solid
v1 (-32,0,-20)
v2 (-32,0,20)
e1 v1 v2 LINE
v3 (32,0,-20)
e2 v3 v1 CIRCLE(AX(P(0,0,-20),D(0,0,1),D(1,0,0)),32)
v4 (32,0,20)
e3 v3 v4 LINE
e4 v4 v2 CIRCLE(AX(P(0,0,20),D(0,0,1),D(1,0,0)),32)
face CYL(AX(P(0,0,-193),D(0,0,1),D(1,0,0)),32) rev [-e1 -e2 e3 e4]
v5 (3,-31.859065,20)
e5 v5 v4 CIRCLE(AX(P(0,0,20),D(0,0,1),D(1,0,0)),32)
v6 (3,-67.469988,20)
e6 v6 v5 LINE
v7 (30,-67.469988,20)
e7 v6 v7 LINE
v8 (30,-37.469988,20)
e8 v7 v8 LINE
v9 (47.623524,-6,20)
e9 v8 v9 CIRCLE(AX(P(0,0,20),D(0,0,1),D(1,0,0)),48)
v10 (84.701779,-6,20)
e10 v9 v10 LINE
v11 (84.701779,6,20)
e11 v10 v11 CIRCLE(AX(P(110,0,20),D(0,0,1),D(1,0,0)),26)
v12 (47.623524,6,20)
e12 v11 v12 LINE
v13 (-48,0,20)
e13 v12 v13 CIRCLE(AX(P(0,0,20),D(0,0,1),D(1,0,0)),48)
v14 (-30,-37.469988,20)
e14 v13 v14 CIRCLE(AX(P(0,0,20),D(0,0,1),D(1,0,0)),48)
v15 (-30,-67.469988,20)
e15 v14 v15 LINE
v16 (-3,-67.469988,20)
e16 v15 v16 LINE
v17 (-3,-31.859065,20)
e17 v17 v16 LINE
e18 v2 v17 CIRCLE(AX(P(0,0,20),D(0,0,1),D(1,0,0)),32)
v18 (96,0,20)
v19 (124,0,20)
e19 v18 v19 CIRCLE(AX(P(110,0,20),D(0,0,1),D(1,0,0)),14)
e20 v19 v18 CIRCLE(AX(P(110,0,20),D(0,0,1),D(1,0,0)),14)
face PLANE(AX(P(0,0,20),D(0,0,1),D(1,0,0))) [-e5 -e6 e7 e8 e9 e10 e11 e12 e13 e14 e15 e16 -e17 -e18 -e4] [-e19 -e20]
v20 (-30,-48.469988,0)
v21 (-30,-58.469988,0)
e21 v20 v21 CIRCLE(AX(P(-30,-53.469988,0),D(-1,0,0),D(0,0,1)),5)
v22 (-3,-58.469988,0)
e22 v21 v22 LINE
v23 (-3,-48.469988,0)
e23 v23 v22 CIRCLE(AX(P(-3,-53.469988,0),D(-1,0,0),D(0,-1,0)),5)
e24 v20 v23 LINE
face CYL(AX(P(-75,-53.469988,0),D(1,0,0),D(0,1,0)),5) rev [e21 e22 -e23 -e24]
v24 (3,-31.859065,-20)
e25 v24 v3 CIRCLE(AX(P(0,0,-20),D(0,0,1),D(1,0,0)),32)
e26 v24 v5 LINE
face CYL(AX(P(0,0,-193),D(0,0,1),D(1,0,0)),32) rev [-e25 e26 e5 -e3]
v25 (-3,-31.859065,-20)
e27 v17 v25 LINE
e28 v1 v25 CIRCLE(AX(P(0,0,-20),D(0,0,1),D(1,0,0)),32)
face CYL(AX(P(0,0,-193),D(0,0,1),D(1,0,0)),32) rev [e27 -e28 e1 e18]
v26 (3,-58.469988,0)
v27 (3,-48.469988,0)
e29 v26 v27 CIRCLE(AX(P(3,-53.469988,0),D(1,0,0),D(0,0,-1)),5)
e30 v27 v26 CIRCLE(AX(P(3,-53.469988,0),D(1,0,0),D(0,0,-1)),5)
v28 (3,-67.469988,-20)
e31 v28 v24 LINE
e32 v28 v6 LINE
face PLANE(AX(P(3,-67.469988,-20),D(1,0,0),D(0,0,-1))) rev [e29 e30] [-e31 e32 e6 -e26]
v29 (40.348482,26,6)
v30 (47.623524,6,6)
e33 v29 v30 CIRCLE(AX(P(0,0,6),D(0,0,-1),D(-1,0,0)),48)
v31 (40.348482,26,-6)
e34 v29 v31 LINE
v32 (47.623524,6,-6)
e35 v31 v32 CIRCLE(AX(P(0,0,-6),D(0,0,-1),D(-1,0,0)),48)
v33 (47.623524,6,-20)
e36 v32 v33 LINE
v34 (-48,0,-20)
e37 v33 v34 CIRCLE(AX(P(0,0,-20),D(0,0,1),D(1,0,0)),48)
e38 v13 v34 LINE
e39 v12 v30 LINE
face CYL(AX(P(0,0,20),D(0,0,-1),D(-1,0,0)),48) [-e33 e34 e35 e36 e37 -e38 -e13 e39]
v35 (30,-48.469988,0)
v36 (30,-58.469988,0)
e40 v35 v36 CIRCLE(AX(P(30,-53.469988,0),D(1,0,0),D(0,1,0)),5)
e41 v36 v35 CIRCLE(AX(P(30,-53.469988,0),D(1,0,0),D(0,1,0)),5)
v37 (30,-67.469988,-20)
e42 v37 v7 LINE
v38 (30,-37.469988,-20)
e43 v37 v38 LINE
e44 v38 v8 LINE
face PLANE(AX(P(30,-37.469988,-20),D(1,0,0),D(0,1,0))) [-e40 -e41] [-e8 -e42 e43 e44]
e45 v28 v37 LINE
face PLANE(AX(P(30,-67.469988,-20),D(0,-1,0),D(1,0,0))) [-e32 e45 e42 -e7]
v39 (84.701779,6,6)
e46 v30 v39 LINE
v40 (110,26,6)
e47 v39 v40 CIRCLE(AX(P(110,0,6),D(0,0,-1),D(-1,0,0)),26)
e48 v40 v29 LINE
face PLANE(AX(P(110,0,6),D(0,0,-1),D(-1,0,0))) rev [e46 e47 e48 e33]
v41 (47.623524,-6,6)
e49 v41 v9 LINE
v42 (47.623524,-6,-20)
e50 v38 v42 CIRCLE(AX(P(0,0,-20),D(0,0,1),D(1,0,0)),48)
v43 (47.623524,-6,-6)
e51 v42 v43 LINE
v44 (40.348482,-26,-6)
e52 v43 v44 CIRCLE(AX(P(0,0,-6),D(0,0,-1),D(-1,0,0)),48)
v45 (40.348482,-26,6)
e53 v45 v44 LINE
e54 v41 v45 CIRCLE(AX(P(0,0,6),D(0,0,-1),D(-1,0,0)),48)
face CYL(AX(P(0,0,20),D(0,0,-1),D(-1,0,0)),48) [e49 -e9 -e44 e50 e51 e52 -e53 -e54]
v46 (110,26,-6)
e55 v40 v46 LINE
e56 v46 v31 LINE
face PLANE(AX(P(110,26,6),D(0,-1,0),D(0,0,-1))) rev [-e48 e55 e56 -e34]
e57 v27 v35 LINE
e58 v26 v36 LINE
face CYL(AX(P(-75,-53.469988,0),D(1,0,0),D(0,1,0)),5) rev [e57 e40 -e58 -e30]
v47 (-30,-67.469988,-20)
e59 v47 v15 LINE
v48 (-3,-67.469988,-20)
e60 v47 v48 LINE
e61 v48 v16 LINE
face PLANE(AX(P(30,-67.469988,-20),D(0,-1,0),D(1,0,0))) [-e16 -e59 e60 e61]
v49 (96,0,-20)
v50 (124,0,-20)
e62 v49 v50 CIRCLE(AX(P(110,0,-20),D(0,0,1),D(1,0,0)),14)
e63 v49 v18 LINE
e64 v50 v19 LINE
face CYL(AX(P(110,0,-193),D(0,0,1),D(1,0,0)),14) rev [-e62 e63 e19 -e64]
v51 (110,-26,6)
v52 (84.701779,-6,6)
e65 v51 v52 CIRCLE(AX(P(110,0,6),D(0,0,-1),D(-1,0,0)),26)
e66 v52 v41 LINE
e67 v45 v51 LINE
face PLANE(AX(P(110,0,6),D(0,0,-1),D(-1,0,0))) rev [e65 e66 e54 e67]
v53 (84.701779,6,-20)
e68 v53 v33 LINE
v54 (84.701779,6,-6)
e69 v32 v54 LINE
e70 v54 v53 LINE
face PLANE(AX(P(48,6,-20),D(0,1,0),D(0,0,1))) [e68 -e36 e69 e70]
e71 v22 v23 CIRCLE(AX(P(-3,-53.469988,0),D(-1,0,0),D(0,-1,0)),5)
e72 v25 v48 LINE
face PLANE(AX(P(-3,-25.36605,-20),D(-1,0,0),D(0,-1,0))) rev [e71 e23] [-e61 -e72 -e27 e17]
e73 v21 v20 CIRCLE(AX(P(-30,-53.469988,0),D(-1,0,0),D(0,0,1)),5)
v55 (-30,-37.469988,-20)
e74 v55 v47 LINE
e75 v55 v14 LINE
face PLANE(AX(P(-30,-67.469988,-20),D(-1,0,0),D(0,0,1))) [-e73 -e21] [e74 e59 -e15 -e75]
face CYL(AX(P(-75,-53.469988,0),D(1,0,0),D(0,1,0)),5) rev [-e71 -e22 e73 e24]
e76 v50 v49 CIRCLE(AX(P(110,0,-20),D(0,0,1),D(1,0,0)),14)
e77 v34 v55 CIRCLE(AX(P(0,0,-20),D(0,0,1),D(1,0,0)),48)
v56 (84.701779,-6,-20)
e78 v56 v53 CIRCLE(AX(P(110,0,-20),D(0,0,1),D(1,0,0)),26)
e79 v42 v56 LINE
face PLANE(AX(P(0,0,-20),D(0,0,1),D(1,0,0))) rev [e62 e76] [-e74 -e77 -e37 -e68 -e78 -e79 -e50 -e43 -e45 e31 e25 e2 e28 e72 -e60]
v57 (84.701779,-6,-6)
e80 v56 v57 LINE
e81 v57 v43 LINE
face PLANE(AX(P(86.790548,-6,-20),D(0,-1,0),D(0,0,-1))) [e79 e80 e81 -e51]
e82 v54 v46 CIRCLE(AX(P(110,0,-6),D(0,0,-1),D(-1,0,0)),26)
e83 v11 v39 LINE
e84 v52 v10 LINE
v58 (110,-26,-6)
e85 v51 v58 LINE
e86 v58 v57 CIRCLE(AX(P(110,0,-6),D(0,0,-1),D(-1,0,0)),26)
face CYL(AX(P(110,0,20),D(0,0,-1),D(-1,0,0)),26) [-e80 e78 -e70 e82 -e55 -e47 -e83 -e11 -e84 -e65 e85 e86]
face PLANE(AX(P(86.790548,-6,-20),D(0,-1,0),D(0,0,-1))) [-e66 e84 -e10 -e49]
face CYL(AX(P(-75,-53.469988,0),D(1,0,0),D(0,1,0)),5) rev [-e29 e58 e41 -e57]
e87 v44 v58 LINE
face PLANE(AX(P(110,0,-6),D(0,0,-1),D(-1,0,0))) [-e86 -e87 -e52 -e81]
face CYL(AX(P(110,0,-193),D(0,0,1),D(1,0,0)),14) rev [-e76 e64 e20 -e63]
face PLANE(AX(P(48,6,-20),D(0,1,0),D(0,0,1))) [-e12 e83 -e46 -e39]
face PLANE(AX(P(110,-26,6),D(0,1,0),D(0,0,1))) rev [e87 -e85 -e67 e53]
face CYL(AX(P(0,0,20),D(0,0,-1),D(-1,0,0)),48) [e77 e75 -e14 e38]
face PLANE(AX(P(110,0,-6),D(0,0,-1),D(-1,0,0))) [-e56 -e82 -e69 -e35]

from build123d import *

# Parameters (mm, degrees)
CLAMP_RING_PROFILE_R       = 48
CLAMP_RING_96_DEPTH        = 20
END_BOSS_PROFILE_R         = 26
END_BOSS_52_DEPTH          = 20
LEVER_WEB_DEPTH            = 40
RIB_A_DEPTH                = 6
RIB_B_DEPTH                = 6
CLAMP_BORE_PROFILE_R       = 32
CLAMP_BORE_DEPTH           = 213
END_BORE_PROFILE_R         = 14
END_BORE_DEPTH             = 213
CLAMP_LUG_DEPTH            = 40
CLAMP_SLOT_DEPTH           = 40
CLAMP_SCREW_HOLE_PROFILE_R = 5
CLAMP_SCREW_HOLE_DEPTH     = 105


with BuildPart() as part:
    # Clamp Ring Profile → Clamp Ring Ø96 (new, symmetric)
    with BuildSketch(Plane.XY):
        Circle(CLAMP_RING_PROFILE_R)
    extrude(amount=CLAMP_RING_96_DEPTH, both=True)



with BuildPart() as body_2:
    # End Boss Profile → End Boss Ø52 (new, symmetric)
    with BuildSketch(Plane.XY):
        with Locations((110, 0)):
            Circle(END_BOSS_PROFILE_R)
    extrude(amount=END_BOSS_52_DEPTH, both=True)


with BuildPart() as part_1:
    add(part.part)

    add(body_2.part)  # Lever Web merges body 2
    # Lever Web Profile → Lever Web (add)
    with BuildSketch(Plane.XY.offset(20)):
        Polygon((48, 6), (86.790548166, 6), (86.790548166, -6), (44, -6), (44, 6), align=None)
    extrude(amount=-LEVER_WEB_DEPTH)

    # Rib A Profile → Rib A (add, symmetric)
    with BuildSketch(Plane.XY):
        with BuildLine():
            Line((110, 26), (40.348482004, 26))
            ThreePointArc((40.348482004, 26), (45.108407669, 16.408277105), (47.623523599, 6))
            Line((47.623523599, 6), (84.701778719, 6))
            ThreePointArc((84.701778719, 6), (93.875484503, 20.396078054), (110, 26))
        make_face()
    extrude(amount=RIB_A_DEPTH, both=True)

    # Rib B Profile → Rib B (add, symmetric)
    with BuildSketch(Plane.XY):
        with BuildLine():
            Line((110, -26), (40.276028999, -26))
            ThreePointArc((40.276028999, -26), (45.014976817, -16.391327753), (47.623523599, -6))
            Line((47.623523599, -6), (84.701778719, -6))
            ThreePointArc((84.701778719, -6), (93.875484503, -20.396078054), (110, -26))
        make_face()
    extrude(amount=RIB_B_DEPTH, both=True)

    # Clamp Bore Profile → Clamp Bore (cut)
    with BuildSketch(Plane.XY.offset(20)):
        Circle(CLAMP_BORE_PROFILE_R)
    extrude(amount=-CLAMP_BORE_DEPTH, mode=Mode.SUBTRACT)

    # End Bore Profile → End Bore (cut)
    with BuildSketch(Plane.XY.offset(20)):
        with Locations((110, 0)):
            Circle(END_BORE_PROFILE_R)
    extrude(amount=-END_BORE_DEPTH, mode=Mode.SUBTRACT)

    # Clamp Lug Profile → Clamp Lug (add)
    with BuildSketch(Plane.XY.offset(20)):
        Polygon((0, -37.46998799), (30, -37.46998799), (30, -67.46998799), (-30, -67.46998799), (-30, -37.46998799), align=None)
    extrude(amount=-CLAMP_LUG_DEPTH)

    # Clamp Slot Profile → Clamp Slot (cut)
    with BuildSketch(Plane.XY.offset(20)):
        Polygon((0, -67.46998799), (3, -67.46998799), (3, -25.366050336), (-3, -25.366050336), (-3, -67.46998799), align=None)
    extrude(amount=-CLAMP_SLOT_DEPTH, mode=Mode.SUBTRACT)

    # Clamp Screw Hole Profile → Clamp Screw Hole (cut)
    with BuildSketch(Plane(origin=(30, 0, 0), x_dir=(0, 0, -1), z_dir=(1, 0, 0))):
        with Locations(Location((0, -53.46998799, 0), (0, 0, 90))):
            Circle(CLAMP_SCREW_HOLE_PROFILE_R)
    extrude(amount=-CLAMP_SCREW_HOLE_DEPTH, mode=Mode.SUBTRACT)


solid = part_1.part
